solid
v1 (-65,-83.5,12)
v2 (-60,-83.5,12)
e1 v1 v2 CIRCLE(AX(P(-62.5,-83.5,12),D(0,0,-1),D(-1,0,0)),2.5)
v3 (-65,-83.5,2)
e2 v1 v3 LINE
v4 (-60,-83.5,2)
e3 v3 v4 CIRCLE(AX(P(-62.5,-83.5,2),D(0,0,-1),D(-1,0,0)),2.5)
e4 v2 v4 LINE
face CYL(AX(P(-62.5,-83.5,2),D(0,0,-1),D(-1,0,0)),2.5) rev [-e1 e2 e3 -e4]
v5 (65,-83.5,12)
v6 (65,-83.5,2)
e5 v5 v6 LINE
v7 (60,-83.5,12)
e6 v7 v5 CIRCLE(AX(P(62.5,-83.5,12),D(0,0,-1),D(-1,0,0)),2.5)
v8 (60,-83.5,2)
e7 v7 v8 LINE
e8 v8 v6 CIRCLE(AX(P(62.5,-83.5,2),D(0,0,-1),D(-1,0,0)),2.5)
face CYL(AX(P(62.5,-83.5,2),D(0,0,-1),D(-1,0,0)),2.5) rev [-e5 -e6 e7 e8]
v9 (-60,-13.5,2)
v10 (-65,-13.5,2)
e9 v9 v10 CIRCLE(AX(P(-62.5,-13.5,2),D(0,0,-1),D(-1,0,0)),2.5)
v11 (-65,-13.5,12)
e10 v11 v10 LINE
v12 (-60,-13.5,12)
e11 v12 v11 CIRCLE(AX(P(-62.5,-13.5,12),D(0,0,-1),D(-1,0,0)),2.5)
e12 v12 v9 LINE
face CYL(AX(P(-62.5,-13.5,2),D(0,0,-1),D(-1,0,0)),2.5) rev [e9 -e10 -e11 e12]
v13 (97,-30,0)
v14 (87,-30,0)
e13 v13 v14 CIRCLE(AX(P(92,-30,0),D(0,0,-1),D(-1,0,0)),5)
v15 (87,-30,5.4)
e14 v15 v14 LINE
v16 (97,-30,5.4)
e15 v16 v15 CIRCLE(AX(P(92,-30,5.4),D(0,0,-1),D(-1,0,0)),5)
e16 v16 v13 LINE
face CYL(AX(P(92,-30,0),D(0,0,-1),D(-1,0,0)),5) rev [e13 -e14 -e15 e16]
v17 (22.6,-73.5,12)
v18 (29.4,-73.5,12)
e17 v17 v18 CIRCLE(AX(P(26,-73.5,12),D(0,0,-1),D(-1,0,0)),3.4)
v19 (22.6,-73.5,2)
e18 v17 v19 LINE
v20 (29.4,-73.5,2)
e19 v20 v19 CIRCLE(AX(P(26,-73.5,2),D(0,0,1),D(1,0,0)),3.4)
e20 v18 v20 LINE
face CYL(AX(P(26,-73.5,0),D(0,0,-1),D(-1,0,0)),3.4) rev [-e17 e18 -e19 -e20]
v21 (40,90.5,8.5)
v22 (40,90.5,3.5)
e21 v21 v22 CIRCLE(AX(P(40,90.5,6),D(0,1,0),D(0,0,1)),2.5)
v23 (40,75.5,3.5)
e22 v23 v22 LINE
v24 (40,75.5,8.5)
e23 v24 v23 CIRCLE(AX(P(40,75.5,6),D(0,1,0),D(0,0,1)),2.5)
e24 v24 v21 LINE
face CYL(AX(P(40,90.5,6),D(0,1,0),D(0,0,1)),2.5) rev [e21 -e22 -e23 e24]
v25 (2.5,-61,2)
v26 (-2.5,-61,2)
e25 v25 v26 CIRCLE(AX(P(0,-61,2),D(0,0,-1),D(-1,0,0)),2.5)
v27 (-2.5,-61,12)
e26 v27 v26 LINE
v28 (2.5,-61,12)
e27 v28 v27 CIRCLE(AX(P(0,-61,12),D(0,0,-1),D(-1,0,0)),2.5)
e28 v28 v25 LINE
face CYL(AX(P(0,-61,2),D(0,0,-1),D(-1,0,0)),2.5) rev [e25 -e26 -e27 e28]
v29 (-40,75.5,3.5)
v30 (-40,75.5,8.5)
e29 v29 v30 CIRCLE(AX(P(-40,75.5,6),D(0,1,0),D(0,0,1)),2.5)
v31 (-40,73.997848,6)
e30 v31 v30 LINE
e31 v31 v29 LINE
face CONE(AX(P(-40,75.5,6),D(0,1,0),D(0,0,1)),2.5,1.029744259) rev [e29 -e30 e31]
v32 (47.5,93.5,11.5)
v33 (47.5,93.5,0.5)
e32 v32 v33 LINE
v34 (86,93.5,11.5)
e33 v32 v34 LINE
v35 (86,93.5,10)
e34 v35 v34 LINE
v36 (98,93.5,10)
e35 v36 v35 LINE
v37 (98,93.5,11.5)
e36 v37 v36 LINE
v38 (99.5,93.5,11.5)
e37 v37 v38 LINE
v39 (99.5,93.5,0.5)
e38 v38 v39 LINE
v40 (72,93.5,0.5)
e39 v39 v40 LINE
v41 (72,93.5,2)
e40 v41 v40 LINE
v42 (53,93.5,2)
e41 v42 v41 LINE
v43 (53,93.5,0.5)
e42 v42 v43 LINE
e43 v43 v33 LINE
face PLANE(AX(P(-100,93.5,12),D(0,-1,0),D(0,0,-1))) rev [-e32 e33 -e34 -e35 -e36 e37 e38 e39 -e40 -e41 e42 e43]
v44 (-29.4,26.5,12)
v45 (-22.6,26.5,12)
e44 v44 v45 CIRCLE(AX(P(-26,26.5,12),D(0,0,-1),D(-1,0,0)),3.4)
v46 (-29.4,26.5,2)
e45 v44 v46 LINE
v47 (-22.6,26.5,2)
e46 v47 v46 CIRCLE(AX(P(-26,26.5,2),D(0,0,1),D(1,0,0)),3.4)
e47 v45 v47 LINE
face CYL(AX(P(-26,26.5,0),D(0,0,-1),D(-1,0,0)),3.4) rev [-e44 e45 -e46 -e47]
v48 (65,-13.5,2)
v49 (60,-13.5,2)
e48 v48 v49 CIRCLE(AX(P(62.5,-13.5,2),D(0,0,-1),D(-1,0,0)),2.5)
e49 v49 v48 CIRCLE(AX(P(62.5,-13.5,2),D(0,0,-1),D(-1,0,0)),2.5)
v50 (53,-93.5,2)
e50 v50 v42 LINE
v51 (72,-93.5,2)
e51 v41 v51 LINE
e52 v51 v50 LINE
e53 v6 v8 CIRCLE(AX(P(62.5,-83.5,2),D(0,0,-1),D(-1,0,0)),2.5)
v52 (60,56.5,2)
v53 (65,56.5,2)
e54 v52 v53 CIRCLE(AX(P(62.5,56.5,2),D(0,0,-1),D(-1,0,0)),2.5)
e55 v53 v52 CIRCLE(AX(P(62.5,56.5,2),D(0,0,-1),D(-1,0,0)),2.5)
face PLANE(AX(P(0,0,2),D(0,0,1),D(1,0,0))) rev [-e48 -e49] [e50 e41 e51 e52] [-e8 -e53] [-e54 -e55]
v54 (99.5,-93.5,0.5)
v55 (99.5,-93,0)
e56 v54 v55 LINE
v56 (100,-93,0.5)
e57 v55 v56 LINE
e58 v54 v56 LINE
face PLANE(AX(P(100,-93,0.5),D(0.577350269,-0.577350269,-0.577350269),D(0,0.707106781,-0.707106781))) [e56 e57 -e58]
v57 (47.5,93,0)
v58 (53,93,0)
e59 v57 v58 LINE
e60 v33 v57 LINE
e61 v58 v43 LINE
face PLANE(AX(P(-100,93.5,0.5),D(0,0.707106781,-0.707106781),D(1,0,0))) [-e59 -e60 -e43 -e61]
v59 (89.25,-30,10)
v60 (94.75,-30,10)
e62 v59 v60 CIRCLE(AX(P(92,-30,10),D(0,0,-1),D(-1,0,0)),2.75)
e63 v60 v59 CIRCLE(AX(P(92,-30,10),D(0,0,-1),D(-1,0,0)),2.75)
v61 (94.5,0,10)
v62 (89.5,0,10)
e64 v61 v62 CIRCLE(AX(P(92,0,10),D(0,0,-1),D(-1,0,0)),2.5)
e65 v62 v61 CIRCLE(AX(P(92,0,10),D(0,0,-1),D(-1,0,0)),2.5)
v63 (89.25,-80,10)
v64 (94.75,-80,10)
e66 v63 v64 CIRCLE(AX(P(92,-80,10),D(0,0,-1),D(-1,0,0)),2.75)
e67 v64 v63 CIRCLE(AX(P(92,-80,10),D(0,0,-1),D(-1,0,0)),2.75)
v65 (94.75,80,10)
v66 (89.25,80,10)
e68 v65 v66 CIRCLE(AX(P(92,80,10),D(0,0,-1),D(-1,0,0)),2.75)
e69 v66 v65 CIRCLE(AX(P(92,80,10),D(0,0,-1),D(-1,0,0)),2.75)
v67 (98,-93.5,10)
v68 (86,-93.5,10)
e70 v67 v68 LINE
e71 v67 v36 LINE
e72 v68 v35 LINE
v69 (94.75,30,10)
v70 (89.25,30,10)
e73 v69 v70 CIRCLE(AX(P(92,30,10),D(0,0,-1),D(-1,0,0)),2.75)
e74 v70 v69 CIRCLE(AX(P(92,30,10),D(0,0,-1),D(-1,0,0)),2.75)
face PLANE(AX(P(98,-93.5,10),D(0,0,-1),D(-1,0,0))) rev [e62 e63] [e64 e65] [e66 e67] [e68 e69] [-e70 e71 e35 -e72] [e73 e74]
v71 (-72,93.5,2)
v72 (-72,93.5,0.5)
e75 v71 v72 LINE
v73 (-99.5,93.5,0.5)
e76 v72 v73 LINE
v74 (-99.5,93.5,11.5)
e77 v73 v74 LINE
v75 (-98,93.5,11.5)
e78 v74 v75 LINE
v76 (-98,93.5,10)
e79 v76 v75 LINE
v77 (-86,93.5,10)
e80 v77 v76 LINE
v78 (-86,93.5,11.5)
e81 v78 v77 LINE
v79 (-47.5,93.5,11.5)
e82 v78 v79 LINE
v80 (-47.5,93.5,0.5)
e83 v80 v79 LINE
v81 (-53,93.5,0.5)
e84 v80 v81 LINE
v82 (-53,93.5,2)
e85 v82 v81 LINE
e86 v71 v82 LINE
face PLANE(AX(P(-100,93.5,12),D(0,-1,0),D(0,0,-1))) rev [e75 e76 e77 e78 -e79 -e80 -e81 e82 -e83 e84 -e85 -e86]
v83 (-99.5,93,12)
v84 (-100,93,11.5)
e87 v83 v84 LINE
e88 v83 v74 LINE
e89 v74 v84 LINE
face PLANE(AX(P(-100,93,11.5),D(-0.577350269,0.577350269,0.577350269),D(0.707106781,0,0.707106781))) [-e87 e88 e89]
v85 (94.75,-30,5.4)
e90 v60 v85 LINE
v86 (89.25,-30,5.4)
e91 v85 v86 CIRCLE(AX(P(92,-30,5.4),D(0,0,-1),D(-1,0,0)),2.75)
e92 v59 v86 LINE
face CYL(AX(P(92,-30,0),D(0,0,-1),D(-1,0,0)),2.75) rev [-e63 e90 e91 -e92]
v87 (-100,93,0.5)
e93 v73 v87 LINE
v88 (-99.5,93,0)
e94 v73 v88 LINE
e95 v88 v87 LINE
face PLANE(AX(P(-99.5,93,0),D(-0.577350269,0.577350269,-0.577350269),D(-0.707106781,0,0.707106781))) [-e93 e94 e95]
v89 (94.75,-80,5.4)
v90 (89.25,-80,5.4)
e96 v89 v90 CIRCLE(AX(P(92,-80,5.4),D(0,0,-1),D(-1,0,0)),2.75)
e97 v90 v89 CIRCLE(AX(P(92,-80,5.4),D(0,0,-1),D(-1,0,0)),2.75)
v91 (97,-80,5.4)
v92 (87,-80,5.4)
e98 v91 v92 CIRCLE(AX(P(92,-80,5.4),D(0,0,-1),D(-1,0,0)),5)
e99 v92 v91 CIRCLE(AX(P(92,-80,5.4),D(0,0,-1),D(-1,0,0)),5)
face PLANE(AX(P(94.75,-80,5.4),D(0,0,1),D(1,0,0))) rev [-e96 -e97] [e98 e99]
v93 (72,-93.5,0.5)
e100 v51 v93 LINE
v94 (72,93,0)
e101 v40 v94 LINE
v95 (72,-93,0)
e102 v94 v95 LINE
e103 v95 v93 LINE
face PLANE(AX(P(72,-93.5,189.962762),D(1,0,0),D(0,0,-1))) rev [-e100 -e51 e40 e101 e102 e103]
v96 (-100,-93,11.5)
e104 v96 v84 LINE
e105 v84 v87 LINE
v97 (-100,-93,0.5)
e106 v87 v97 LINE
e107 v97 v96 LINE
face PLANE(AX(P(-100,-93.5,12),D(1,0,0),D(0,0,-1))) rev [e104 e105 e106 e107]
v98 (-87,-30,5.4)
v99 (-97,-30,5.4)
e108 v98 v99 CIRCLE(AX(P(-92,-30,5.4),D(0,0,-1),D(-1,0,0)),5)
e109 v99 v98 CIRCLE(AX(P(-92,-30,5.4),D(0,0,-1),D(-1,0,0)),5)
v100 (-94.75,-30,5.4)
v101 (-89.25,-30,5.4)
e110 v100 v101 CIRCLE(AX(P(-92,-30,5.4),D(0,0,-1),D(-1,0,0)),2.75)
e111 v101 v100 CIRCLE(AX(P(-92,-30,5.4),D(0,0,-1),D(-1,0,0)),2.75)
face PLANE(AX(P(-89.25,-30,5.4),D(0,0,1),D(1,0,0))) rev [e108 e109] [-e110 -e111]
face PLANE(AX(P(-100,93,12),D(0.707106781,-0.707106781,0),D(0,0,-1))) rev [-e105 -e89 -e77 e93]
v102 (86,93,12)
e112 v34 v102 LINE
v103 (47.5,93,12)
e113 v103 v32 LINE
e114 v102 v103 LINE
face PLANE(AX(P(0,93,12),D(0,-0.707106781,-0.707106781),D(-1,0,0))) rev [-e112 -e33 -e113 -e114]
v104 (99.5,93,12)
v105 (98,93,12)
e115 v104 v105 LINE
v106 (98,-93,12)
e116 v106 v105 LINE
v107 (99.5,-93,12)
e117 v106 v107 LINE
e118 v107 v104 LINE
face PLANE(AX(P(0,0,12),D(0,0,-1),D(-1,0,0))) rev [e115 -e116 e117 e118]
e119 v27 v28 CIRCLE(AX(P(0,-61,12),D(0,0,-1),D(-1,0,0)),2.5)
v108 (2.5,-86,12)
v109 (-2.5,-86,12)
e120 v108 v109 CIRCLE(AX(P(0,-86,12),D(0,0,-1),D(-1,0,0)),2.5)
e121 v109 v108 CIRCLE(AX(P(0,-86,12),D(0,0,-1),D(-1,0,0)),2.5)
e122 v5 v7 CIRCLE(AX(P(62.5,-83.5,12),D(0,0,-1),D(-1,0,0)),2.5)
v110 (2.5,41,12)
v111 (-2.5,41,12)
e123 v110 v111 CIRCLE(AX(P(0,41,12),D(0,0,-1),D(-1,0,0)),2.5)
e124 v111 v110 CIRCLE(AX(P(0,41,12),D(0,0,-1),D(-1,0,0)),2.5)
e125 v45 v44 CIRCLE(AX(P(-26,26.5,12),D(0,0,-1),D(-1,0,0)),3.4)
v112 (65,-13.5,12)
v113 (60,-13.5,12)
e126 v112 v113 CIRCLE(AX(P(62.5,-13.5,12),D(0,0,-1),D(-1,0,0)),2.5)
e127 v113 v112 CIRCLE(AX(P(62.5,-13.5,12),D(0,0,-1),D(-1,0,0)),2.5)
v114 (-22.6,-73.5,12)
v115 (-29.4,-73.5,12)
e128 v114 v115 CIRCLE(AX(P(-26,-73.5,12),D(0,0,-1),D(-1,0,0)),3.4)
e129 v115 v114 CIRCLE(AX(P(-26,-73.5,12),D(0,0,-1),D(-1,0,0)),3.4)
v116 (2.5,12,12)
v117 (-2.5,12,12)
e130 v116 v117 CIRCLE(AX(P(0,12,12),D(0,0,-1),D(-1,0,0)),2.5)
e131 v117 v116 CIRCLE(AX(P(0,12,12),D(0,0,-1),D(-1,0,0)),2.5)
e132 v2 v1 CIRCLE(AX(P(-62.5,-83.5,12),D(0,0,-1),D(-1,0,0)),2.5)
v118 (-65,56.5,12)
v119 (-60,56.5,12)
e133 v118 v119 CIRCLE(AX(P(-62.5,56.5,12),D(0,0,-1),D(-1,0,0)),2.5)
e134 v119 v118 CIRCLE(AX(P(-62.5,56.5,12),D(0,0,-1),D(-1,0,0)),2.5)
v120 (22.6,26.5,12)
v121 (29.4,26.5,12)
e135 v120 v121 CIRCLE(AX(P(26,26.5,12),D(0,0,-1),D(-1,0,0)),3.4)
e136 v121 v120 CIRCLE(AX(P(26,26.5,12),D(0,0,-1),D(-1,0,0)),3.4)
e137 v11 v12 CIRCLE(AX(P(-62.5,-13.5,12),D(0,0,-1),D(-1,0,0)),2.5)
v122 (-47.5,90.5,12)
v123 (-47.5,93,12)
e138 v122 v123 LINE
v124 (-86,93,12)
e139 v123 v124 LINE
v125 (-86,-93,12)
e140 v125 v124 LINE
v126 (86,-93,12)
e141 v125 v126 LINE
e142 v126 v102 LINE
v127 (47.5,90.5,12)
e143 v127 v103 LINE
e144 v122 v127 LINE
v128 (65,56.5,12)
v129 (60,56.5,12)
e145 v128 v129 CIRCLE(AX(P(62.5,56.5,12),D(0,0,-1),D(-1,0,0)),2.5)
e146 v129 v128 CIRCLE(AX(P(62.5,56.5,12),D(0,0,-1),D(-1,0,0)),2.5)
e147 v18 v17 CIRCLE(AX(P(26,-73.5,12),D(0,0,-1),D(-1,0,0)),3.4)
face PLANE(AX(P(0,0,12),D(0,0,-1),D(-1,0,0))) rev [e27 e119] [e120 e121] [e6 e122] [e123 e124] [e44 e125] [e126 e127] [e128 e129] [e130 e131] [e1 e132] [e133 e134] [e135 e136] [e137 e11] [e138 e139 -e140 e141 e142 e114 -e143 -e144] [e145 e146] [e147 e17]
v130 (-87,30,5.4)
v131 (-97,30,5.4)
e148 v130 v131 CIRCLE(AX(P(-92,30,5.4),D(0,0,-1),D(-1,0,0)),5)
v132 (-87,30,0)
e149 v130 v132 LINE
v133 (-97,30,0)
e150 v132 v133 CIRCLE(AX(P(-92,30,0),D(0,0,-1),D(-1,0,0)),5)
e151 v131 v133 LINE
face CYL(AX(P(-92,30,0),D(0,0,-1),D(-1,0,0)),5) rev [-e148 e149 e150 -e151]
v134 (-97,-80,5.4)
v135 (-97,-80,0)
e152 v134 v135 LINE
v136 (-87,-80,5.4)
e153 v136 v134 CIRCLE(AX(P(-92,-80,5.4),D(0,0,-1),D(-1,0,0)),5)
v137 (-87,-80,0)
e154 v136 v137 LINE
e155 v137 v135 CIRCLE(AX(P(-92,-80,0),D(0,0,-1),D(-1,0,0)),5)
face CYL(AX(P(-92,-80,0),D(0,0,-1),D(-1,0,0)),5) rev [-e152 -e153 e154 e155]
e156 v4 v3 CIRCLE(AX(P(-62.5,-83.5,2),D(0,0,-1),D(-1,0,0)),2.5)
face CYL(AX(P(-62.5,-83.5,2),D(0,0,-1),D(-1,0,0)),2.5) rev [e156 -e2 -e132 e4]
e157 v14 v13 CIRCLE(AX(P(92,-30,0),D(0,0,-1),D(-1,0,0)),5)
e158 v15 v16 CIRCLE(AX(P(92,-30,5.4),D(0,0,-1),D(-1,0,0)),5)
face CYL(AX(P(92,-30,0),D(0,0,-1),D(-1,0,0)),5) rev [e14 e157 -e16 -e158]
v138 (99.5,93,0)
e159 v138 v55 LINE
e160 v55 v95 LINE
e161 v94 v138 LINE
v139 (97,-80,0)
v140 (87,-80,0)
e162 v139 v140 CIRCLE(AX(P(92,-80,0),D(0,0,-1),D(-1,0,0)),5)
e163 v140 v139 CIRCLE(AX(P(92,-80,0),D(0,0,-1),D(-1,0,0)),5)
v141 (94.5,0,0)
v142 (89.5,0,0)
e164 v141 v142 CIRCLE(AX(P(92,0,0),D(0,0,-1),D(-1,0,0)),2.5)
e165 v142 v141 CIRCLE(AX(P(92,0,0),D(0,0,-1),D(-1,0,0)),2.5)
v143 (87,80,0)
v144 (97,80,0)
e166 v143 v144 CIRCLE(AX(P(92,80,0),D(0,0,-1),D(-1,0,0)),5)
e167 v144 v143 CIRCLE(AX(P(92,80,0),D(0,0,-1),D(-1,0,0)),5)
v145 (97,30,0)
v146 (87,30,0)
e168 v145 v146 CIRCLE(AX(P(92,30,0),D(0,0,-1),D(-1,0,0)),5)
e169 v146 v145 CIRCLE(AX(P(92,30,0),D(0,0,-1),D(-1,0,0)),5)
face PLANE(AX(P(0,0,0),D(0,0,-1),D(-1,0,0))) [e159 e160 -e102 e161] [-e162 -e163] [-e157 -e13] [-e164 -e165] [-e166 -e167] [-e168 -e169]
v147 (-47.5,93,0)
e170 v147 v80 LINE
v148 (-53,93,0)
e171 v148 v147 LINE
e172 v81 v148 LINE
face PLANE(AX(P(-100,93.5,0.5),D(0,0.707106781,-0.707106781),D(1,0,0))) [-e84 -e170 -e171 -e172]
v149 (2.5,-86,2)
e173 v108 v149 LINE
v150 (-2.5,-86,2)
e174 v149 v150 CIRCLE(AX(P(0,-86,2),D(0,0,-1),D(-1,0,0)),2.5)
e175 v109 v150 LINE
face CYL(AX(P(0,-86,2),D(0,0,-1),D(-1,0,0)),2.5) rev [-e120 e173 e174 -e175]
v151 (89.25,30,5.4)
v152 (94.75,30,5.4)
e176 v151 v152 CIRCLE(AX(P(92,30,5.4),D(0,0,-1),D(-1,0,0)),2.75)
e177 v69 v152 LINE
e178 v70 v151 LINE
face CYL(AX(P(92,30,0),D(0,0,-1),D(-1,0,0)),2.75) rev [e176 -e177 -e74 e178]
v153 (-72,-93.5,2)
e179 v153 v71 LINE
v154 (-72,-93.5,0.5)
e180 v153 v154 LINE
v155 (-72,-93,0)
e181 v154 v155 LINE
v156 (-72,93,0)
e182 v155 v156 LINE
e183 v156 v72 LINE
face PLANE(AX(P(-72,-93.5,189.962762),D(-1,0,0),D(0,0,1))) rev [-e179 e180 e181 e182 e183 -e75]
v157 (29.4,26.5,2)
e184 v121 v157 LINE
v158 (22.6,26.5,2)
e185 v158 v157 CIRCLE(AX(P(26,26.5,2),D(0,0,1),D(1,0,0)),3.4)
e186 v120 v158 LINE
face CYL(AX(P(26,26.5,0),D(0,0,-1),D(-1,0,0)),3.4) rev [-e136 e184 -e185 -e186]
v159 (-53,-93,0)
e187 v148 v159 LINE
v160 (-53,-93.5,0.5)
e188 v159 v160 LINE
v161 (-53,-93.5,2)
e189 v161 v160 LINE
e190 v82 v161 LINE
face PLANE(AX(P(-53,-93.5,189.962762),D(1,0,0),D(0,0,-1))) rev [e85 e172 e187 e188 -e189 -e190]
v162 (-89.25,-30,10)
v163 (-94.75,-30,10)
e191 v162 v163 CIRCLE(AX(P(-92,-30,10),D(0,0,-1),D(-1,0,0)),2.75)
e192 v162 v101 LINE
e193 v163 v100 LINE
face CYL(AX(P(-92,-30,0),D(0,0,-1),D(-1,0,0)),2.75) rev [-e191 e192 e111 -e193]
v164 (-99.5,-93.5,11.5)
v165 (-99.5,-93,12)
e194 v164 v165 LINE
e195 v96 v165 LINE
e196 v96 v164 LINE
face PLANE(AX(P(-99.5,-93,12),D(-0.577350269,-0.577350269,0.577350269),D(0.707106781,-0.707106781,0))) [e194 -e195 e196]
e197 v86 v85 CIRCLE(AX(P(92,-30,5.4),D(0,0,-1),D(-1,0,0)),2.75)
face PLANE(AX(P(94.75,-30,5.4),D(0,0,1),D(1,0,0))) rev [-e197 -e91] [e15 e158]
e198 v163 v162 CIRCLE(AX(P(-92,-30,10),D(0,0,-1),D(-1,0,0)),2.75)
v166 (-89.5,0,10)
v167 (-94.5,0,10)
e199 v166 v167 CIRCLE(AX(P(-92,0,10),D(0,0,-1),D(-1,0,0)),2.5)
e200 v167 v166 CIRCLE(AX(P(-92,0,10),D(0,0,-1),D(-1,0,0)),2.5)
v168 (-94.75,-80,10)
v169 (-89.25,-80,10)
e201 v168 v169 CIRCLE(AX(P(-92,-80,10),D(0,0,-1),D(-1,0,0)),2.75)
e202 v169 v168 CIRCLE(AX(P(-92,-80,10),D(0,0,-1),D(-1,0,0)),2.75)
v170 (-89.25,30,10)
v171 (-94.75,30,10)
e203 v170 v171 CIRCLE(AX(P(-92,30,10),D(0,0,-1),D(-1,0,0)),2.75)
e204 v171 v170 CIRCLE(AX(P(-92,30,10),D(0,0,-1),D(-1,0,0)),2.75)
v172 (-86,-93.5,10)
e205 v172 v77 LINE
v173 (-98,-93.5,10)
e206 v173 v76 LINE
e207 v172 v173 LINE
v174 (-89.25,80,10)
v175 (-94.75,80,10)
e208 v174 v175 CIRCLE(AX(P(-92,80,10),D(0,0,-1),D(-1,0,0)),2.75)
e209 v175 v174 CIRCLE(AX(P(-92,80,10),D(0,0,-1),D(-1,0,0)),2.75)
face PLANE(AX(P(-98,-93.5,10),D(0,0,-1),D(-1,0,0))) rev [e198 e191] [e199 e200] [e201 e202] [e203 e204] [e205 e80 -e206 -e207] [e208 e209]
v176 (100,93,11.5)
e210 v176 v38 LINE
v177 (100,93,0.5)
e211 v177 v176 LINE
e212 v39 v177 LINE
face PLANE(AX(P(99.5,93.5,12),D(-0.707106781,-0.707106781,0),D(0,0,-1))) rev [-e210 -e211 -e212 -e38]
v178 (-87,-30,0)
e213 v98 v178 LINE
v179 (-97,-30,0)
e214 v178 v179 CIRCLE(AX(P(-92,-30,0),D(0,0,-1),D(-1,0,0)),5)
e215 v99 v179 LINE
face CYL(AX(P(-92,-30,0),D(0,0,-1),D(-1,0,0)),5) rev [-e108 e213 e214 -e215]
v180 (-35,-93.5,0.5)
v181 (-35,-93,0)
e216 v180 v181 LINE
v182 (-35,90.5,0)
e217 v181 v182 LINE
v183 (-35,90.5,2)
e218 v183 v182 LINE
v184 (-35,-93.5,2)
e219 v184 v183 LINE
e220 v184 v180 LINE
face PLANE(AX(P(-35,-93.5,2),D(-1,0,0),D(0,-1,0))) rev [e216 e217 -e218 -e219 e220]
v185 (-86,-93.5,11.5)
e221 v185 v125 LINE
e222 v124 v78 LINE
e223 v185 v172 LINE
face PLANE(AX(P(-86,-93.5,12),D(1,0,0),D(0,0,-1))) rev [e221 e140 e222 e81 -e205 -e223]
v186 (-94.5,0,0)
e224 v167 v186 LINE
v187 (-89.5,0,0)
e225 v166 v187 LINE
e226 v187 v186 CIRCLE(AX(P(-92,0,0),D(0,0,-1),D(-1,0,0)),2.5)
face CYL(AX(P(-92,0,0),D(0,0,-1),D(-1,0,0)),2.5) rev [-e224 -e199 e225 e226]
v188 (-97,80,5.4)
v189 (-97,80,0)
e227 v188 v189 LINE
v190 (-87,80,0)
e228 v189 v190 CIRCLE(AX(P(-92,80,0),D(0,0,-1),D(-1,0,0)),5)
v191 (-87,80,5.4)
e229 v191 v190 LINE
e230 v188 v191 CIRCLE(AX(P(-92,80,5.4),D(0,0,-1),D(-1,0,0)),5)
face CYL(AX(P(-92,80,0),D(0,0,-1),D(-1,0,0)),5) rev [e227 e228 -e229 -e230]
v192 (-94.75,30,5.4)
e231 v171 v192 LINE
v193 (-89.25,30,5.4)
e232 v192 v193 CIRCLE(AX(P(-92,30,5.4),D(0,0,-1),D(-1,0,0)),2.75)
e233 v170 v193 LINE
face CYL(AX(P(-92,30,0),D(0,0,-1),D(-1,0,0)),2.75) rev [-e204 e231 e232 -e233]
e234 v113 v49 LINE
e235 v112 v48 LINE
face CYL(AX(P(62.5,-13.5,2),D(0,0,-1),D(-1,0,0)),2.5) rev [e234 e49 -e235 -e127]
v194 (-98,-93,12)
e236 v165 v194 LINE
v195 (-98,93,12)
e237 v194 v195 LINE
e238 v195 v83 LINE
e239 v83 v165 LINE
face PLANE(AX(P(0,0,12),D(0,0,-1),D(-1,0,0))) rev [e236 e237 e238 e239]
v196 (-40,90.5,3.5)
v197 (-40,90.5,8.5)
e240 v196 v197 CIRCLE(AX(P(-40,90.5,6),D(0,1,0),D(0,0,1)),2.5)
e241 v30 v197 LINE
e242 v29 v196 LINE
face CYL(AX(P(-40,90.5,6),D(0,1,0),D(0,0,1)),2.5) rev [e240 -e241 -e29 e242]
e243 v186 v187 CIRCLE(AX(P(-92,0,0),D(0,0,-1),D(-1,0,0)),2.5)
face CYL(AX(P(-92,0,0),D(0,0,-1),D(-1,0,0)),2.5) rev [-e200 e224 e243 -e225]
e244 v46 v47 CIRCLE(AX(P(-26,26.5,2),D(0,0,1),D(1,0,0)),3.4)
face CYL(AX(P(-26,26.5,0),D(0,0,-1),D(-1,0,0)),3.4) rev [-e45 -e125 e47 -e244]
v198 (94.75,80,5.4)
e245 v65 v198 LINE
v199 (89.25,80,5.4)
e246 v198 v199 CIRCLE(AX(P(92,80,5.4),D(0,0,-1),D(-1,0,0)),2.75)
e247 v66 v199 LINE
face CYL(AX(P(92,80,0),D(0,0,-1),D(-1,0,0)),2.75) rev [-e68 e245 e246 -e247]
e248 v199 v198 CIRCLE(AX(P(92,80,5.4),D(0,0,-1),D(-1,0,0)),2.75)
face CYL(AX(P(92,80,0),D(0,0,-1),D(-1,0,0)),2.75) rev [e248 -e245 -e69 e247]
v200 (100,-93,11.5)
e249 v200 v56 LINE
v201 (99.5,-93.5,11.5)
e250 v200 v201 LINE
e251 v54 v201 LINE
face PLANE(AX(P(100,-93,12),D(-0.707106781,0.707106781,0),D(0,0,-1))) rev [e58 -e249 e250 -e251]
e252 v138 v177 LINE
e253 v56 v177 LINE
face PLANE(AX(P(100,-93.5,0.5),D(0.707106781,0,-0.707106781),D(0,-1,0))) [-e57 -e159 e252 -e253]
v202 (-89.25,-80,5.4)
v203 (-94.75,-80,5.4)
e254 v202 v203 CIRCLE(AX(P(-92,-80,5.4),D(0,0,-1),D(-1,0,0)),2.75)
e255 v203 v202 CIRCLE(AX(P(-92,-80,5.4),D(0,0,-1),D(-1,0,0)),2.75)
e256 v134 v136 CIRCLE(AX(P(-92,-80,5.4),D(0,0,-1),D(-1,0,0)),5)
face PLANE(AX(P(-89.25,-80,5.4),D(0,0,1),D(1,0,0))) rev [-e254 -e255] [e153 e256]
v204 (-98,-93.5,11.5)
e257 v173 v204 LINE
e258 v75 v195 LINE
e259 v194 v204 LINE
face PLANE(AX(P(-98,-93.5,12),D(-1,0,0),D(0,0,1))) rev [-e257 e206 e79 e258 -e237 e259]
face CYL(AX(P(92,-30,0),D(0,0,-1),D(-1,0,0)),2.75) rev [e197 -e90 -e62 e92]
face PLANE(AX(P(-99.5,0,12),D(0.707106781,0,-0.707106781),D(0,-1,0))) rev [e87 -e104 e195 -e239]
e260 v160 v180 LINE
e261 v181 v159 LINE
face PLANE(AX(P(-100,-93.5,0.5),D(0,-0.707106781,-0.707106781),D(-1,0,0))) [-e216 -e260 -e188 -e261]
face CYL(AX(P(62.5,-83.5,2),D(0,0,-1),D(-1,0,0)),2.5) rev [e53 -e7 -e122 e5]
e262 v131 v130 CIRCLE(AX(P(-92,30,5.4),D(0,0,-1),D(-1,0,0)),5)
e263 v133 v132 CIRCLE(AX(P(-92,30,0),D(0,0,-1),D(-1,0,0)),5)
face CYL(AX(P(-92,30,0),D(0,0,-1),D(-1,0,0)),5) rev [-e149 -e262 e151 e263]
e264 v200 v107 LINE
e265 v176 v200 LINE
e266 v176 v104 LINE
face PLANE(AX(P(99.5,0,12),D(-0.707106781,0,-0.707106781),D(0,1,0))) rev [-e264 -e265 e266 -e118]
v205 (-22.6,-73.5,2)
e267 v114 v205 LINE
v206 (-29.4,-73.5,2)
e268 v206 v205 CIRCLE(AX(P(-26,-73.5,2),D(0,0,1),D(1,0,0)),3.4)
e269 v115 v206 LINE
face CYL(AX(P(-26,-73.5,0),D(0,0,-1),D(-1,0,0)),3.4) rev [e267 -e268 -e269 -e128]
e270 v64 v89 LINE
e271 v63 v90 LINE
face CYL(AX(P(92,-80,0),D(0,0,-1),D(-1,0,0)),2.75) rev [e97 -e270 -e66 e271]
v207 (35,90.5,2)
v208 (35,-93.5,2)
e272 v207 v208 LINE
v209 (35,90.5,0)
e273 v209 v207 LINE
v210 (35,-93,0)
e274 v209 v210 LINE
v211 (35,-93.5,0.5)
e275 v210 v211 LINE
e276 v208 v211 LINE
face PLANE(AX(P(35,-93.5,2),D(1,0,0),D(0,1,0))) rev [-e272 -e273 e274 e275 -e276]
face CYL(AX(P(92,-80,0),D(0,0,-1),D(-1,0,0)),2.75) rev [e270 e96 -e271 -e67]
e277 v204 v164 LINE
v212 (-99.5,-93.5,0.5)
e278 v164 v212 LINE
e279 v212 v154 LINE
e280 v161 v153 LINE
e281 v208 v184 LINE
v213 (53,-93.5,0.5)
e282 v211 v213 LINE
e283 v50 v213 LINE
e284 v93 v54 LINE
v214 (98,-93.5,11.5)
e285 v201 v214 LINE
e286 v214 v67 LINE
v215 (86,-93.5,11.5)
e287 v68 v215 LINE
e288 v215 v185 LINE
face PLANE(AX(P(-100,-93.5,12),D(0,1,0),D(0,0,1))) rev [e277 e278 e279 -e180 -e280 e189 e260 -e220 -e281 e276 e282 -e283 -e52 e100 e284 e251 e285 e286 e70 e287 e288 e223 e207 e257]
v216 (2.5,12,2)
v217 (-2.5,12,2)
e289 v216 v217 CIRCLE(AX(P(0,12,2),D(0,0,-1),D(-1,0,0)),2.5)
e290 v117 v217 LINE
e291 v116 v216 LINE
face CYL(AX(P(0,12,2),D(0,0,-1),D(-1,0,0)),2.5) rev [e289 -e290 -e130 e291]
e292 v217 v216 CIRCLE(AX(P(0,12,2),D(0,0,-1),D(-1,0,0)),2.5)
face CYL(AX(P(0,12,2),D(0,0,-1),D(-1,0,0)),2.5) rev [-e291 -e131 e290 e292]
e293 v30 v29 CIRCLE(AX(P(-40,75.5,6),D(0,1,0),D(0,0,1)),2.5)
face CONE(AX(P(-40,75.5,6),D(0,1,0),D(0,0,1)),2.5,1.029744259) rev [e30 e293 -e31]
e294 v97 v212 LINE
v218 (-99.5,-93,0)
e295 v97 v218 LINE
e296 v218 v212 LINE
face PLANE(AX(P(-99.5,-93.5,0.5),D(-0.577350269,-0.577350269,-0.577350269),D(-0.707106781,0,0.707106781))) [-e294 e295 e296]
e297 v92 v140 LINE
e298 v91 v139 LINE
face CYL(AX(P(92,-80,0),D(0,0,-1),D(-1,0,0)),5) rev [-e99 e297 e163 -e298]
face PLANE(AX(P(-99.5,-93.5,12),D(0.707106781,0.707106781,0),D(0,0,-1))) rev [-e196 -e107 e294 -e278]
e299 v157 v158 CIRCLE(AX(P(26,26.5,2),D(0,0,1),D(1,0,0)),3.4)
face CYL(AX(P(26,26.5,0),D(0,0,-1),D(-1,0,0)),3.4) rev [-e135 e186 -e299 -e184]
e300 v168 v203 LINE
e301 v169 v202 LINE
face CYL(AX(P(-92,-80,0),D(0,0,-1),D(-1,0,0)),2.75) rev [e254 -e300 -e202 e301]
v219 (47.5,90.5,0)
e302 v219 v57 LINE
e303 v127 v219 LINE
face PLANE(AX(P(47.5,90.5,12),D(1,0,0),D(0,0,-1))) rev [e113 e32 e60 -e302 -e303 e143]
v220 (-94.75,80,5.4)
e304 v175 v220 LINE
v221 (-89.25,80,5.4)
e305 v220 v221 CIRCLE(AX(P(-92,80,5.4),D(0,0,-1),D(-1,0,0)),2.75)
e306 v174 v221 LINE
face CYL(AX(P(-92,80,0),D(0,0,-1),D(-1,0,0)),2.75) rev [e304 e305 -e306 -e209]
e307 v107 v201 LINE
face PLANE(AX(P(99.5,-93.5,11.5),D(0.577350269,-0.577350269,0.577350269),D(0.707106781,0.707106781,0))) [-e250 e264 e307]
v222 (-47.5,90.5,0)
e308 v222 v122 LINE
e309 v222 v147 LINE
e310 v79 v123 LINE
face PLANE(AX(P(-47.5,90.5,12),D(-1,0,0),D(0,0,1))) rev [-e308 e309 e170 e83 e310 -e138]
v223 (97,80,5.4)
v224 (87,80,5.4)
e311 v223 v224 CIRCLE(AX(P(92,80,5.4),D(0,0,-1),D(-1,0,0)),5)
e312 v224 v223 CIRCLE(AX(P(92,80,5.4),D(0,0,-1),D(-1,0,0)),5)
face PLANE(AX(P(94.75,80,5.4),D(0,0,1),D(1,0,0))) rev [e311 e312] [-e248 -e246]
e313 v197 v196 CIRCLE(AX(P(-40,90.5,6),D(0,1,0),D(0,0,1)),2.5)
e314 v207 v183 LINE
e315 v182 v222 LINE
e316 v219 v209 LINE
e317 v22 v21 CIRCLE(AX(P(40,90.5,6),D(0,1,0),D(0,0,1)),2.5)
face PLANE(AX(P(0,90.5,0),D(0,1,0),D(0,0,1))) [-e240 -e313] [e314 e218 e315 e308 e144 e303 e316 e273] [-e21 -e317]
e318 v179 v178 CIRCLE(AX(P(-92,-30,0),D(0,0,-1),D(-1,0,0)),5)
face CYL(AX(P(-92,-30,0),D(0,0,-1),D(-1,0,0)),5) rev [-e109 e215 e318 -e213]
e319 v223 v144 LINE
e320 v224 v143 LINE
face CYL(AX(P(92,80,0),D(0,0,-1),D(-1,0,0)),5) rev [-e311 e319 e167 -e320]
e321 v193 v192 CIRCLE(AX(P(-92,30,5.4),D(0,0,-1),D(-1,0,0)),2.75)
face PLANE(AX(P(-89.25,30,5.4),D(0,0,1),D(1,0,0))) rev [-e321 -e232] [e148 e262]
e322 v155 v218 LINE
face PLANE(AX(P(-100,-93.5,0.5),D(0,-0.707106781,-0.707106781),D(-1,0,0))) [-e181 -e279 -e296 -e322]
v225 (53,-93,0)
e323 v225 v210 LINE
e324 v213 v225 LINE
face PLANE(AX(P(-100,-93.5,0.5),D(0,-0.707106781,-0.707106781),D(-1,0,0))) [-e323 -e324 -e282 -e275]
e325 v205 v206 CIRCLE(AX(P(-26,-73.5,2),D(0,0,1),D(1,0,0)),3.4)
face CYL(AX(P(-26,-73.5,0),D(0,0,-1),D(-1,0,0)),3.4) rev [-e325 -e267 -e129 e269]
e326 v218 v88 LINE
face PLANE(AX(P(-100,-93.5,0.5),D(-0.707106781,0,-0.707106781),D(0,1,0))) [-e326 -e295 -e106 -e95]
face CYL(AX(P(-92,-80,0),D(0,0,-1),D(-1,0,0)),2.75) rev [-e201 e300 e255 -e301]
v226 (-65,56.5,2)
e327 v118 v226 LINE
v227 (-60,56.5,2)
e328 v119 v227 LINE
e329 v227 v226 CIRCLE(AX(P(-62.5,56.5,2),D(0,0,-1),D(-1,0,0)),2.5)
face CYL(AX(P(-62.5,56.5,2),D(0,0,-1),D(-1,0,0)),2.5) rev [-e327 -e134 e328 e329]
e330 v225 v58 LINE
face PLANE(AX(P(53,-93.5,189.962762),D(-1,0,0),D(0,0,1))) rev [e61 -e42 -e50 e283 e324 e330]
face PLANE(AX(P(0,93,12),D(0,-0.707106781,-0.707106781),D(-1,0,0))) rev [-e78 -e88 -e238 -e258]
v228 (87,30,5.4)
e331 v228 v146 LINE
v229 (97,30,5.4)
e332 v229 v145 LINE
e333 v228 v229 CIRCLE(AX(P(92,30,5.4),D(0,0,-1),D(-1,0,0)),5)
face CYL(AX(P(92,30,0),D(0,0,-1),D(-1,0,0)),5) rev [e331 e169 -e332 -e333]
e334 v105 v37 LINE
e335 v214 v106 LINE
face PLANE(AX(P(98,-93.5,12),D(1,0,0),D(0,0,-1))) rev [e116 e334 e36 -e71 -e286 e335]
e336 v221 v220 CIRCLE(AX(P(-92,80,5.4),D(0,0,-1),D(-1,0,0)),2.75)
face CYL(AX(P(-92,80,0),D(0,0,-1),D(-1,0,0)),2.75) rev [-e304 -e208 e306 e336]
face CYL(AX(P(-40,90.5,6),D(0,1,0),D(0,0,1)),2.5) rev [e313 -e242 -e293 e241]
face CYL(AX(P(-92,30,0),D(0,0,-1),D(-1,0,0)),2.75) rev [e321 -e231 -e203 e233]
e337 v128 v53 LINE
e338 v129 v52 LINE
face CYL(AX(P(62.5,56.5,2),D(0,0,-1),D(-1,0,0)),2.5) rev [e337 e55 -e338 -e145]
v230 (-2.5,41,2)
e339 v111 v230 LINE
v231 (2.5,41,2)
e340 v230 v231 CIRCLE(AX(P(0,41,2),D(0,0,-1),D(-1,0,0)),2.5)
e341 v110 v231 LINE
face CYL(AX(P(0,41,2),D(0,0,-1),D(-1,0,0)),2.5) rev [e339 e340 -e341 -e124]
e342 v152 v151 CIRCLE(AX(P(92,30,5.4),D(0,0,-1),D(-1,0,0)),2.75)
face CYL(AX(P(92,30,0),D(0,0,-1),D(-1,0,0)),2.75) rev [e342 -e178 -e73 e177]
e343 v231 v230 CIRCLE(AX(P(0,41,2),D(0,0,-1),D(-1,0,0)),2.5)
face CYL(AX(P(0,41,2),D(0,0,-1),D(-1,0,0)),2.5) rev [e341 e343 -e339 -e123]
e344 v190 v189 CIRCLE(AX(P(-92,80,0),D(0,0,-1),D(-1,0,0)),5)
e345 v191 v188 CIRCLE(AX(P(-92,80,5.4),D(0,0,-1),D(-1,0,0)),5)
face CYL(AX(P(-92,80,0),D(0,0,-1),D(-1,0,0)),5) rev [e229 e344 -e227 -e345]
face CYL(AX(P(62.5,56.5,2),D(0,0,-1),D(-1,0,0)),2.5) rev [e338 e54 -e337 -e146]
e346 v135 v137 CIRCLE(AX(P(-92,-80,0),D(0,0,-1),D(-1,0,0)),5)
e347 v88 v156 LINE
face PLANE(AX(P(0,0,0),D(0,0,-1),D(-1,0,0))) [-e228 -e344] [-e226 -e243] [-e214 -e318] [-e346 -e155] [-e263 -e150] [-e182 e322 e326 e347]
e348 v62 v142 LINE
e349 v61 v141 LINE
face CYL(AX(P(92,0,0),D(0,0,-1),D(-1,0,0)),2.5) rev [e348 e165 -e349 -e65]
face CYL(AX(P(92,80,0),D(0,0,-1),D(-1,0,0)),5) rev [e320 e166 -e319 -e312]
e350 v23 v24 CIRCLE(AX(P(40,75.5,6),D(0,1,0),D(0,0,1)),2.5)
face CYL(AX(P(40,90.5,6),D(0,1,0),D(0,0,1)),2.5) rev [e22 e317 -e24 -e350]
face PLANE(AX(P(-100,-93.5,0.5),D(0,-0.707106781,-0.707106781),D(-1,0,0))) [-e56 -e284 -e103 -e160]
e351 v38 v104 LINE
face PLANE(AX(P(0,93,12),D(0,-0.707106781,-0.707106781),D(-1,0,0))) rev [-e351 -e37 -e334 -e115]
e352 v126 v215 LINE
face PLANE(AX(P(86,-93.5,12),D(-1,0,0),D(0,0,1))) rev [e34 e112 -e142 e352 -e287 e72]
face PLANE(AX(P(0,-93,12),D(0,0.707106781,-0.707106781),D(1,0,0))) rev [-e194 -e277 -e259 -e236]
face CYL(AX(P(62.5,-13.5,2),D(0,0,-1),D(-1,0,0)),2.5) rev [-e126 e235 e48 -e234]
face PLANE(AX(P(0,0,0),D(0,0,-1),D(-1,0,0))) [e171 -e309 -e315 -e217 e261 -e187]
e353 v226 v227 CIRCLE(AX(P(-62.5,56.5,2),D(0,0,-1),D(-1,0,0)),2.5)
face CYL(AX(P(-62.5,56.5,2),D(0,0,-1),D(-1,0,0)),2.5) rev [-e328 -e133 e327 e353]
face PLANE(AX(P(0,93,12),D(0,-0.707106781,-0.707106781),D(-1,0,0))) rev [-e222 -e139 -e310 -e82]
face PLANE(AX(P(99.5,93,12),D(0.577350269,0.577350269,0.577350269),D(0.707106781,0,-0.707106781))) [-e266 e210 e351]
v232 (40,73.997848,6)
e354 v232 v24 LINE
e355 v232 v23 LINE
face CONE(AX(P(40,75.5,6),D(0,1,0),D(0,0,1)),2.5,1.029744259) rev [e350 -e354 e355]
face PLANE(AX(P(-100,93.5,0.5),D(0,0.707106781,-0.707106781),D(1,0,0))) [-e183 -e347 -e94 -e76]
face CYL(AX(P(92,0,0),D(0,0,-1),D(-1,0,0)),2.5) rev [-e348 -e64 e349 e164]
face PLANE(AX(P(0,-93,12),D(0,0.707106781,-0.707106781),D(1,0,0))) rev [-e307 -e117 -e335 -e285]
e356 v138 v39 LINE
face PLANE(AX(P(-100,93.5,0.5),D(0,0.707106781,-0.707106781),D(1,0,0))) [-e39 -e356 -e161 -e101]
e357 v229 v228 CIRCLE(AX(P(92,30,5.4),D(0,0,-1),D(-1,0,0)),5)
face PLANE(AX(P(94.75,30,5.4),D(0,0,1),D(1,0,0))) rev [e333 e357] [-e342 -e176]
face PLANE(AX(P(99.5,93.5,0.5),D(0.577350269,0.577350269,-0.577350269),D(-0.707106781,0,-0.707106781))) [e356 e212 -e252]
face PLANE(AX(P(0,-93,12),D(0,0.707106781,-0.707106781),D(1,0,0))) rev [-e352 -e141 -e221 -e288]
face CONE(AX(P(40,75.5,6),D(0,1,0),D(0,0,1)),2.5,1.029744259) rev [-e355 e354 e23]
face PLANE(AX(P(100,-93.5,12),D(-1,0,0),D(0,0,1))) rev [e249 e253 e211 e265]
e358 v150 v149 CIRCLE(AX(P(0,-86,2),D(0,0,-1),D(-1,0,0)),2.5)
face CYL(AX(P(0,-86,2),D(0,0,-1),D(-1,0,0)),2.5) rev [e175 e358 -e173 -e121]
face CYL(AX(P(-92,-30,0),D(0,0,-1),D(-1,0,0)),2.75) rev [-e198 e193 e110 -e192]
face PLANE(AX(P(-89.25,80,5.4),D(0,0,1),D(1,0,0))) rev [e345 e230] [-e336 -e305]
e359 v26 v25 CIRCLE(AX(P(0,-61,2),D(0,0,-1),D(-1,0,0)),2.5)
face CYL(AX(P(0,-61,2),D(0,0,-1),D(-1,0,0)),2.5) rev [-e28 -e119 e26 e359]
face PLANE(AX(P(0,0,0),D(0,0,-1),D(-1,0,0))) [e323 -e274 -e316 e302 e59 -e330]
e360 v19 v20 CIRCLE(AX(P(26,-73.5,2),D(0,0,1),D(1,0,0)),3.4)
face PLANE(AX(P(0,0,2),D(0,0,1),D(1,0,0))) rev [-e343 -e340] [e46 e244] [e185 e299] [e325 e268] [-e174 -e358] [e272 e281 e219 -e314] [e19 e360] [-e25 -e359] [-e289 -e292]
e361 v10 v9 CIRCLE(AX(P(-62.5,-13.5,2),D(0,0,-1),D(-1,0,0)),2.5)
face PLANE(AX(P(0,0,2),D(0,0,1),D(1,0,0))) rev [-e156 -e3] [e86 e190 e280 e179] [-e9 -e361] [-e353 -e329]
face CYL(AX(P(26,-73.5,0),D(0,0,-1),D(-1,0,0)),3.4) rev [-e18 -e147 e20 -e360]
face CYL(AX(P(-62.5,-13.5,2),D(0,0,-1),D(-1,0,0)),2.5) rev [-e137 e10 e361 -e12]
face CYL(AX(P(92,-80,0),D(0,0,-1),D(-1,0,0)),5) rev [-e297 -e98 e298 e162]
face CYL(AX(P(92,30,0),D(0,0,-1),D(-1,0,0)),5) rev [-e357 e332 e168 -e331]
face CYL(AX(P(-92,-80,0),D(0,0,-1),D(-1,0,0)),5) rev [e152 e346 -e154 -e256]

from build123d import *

# Parameters (mm, degrees)
SKETCH_1_W                   = 200
SKETCH_1_H                   = 187
EXTRUDE_1_DEPTH              = 12
SKETCH_4_W                   = 70
SKETCH_4_H                   = 187
CUT_EXTRUDE_3_DEPTH          = 2
SKETCH_5_W                   = 12
SKETCH_5_H                   = 2
CUT_EXTRUDE_4_DEPTH          = 213.398210915
SKETCH_6_W                   = 95
SKETCH_6_H                   = 12
CUT_EXTRUDE_5_DEPTH          = 3
HOLE_WIZARD_M6_1_D           = 5
HOLE_WIZARD_M6_1_DEPTH       = 15
HOLE_WIZARD_M6_1_TIP         = 1.502151548
SKETCH_9_W                   = 19
SKETCH_9_H                   = 187
CUT_EXTRUDE_6_DEPTH          = 2
HOLE_WIZARD_M8_1_D           = 6.8
MM_0_D                       = 5
HOLE_WIZARD_M6_2_D           = 5
MM_1_D                       = 5
HOLE_WIZARD_M5_1_D           = 5.5
HOLE_WIZARD_M5_1_CBORE_D     = 10
HOLE_WIZARD_M5_1_CBORE_DEPTH = 5.4
MM_2_D                       = 5
CHAMFER_1_SIZE               = 0.5


with BuildPart() as part:
    # 草图1 → 凸台-拉伸1 (new body)
    with BuildSketch(Plane.XY):
        Rectangle(SKETCH_1_W, SKETCH_1_H)
    extrude(amount=EXTRUDE_1_DEPTH)

    # 草图4 → 切除-拉伸3 (cut)
    with BuildSketch(Plane(origin=(0, 0, 0), x_dir=(-1, 0, 0), z_dir=(0, 0, -1))):
        Rectangle(SKETCH_4_W, SKETCH_4_H)
    extrude(amount=-CUT_EXTRUDE_3_DEPTH, mode=Mode.SUBTRACT)

    # 草图5 → 切除-拉伸4 (cut, through all)
    with BuildSketch(Plane(origin=(0, 93.5, 0), x_dir=(1, 0, 0), z_dir=(0, 1, 0))):
        with Locations((-92, -11)):
            Rectangle(SKETCH_5_W, SKETCH_5_H)
        with Locations((92, -11)):
            Rectangle(SKETCH_5_W, SKETCH_5_H)
    extrude(amount=-CUT_EXTRUDE_4_DEPTH, mode=Mode.SUBTRACT)

    # 草图6 → 切除-拉伸5 (cut)
    with BuildSketch(Plane(origin=(0, 93.5, 0), x_dir=(1, 0, 0), z_dir=(0, 1, 0))):
        with Locations((0, -6)):
            Rectangle(SKETCH_6_W, SKETCH_6_H)
    extrude(amount=-CUT_EXTRUDE_5_DEPTH, mode=Mode.SUBTRACT)

    # M6 螺纹孔1
    with Locations(Plane(origin=(0, 90.5, 0), x_dir=(1, 0, 0), z_dir=(0, 1, 0))):
        with Locations((-40, -6), (40, -6)):
            Hole(HOLE_WIZARD_M6_1_D / 2, depth=HOLE_WIZARD_M6_1_DEPTH)
            with Locations((0, 0, -(HOLE_WIZARD_M6_1_DEPTH + HOLE_WIZARD_M6_1_TIP / 2))):  # 118° drill point
                Cone(0, HOLE_WIZARD_M6_1_D / 2, HOLE_WIZARD_M6_1_TIP, mode=Mode.SUBTRACT)

    # 草图9 → 切除-拉伸6 (cut)
    with BuildSketch(Plane(origin=(0, 0, 0), x_dir=(-1, 0, 0), z_dir=(0, 0, -1))):
        with Locations((-62.5, 0)):
            Rectangle(SKETCH_9_W, SKETCH_9_H)
        with Locations((62.5, 0)):
            Rectangle(SKETCH_9_W, SKETCH_9_H)
    extrude(amount=-CUT_EXTRUDE_6_DEPTH, mode=Mode.SUBTRACT)

    # M8 螺纹孔1 (through all)
    with Locations(Plane(origin=(0, 0, 0), x_dir=(-1, 0, 0), z_dir=(0, 0, -1))):
        with Locations((26, -73.5), (-26, -73.5), (26, 26.5), (-26, 26.5)):
            Hole(HOLE_WIZARD_M8_1_D / 2)

    # 大小mm 暗销孔0 (through all)
    with Locations(Plane(origin=(0, 0, 2), x_dir=(-1, 0, 0), z_dir=(0, 0, -1))):
        with Locations((0, -86), (0, -61), (0, 12), (0, 41)):
            Hole(MM_0_D / 2)

    # M6 螺纹孔2 (through all)
    with Locations(Plane(origin=(0, 0, 2), x_dir=(-1, 0, 0), z_dir=(0, 0, -1))):
        with Locations((62.5, -83.5), (62.5, 56.5), (-62.5, 56.5), (-62.5, -83.5)):
            Hole(HOLE_WIZARD_M6_2_D / 2)

    # 大小mm 暗销孔1 (through all)
    with Locations(Plane(origin=(0, 0, 2), x_dir=(-1, 0, 0), z_dir=(0, 0, -1))):
        with Locations((-62.5, -13.5), (62.5, -13.5)):
            Hole(MM_1_D / 2)

    # M5 六角凹头螺钉的柱形沉头孔1 (through all)
    with Locations(Plane(origin=(0, 0, 0), x_dir=(-1, 0, 0), z_dir=(0, 0, -1))):
        with Locations((-92, 80), (-92, -80), (-92, 30), (-92, -30), (92, -30), (92, 30), (92, -80), (92, 80)):
            CounterBoreHole(HOLE_WIZARD_M5_1_D / 2, HOLE_WIZARD_M5_1_CBORE_D / 2, HOLE_WIZARD_M5_1_CBORE_DEPTH)

    # 大小mm 暗销孔2 (through all)
    with Locations(Plane(origin=(0, 0, 0), x_dir=(-1, 0, 0), z_dir=(0, 0, -1))):
        with Locations((92, 0), (-92, 0)):
            Hole(MM_2_D / 2)

    # 倒角1
    chamfer_1_edges = [part.edges().sort_by_distance(p)[0] for p in [
        (-100, 0, 12),
        (50.25, 93.5, 0),
        (-99, -93.5, 12),
        (44, -93.5, 0),
        (66.75, 93.5, 12),
        (-99, 93.5, 12),
        (0, -93.5, 12),
        (99, -93.5, 12),
        (100, 0, 12),
        (-86, -93.5, 0),
        (-100, 0, 0),
        (86, 93.5, 0),
        (100, 0, 0),
        (-50.25, 93.5, 0),
        (-66.75, 93.5, 12),
        (99, 93.5, 12),
        (100, -93.5, 6),
        (-100, -93.5, 6),
        (-100, 93.5, 6),
        (100, 93.5, 6),
        (-44, -93.5, 0),
        (-86, 93.5, 0),
        (86, -93.5, 0),
    ]]
    chamfer(chamfer_1_edges, length=CHAMFER_1_SIZE)


solid = part.part
